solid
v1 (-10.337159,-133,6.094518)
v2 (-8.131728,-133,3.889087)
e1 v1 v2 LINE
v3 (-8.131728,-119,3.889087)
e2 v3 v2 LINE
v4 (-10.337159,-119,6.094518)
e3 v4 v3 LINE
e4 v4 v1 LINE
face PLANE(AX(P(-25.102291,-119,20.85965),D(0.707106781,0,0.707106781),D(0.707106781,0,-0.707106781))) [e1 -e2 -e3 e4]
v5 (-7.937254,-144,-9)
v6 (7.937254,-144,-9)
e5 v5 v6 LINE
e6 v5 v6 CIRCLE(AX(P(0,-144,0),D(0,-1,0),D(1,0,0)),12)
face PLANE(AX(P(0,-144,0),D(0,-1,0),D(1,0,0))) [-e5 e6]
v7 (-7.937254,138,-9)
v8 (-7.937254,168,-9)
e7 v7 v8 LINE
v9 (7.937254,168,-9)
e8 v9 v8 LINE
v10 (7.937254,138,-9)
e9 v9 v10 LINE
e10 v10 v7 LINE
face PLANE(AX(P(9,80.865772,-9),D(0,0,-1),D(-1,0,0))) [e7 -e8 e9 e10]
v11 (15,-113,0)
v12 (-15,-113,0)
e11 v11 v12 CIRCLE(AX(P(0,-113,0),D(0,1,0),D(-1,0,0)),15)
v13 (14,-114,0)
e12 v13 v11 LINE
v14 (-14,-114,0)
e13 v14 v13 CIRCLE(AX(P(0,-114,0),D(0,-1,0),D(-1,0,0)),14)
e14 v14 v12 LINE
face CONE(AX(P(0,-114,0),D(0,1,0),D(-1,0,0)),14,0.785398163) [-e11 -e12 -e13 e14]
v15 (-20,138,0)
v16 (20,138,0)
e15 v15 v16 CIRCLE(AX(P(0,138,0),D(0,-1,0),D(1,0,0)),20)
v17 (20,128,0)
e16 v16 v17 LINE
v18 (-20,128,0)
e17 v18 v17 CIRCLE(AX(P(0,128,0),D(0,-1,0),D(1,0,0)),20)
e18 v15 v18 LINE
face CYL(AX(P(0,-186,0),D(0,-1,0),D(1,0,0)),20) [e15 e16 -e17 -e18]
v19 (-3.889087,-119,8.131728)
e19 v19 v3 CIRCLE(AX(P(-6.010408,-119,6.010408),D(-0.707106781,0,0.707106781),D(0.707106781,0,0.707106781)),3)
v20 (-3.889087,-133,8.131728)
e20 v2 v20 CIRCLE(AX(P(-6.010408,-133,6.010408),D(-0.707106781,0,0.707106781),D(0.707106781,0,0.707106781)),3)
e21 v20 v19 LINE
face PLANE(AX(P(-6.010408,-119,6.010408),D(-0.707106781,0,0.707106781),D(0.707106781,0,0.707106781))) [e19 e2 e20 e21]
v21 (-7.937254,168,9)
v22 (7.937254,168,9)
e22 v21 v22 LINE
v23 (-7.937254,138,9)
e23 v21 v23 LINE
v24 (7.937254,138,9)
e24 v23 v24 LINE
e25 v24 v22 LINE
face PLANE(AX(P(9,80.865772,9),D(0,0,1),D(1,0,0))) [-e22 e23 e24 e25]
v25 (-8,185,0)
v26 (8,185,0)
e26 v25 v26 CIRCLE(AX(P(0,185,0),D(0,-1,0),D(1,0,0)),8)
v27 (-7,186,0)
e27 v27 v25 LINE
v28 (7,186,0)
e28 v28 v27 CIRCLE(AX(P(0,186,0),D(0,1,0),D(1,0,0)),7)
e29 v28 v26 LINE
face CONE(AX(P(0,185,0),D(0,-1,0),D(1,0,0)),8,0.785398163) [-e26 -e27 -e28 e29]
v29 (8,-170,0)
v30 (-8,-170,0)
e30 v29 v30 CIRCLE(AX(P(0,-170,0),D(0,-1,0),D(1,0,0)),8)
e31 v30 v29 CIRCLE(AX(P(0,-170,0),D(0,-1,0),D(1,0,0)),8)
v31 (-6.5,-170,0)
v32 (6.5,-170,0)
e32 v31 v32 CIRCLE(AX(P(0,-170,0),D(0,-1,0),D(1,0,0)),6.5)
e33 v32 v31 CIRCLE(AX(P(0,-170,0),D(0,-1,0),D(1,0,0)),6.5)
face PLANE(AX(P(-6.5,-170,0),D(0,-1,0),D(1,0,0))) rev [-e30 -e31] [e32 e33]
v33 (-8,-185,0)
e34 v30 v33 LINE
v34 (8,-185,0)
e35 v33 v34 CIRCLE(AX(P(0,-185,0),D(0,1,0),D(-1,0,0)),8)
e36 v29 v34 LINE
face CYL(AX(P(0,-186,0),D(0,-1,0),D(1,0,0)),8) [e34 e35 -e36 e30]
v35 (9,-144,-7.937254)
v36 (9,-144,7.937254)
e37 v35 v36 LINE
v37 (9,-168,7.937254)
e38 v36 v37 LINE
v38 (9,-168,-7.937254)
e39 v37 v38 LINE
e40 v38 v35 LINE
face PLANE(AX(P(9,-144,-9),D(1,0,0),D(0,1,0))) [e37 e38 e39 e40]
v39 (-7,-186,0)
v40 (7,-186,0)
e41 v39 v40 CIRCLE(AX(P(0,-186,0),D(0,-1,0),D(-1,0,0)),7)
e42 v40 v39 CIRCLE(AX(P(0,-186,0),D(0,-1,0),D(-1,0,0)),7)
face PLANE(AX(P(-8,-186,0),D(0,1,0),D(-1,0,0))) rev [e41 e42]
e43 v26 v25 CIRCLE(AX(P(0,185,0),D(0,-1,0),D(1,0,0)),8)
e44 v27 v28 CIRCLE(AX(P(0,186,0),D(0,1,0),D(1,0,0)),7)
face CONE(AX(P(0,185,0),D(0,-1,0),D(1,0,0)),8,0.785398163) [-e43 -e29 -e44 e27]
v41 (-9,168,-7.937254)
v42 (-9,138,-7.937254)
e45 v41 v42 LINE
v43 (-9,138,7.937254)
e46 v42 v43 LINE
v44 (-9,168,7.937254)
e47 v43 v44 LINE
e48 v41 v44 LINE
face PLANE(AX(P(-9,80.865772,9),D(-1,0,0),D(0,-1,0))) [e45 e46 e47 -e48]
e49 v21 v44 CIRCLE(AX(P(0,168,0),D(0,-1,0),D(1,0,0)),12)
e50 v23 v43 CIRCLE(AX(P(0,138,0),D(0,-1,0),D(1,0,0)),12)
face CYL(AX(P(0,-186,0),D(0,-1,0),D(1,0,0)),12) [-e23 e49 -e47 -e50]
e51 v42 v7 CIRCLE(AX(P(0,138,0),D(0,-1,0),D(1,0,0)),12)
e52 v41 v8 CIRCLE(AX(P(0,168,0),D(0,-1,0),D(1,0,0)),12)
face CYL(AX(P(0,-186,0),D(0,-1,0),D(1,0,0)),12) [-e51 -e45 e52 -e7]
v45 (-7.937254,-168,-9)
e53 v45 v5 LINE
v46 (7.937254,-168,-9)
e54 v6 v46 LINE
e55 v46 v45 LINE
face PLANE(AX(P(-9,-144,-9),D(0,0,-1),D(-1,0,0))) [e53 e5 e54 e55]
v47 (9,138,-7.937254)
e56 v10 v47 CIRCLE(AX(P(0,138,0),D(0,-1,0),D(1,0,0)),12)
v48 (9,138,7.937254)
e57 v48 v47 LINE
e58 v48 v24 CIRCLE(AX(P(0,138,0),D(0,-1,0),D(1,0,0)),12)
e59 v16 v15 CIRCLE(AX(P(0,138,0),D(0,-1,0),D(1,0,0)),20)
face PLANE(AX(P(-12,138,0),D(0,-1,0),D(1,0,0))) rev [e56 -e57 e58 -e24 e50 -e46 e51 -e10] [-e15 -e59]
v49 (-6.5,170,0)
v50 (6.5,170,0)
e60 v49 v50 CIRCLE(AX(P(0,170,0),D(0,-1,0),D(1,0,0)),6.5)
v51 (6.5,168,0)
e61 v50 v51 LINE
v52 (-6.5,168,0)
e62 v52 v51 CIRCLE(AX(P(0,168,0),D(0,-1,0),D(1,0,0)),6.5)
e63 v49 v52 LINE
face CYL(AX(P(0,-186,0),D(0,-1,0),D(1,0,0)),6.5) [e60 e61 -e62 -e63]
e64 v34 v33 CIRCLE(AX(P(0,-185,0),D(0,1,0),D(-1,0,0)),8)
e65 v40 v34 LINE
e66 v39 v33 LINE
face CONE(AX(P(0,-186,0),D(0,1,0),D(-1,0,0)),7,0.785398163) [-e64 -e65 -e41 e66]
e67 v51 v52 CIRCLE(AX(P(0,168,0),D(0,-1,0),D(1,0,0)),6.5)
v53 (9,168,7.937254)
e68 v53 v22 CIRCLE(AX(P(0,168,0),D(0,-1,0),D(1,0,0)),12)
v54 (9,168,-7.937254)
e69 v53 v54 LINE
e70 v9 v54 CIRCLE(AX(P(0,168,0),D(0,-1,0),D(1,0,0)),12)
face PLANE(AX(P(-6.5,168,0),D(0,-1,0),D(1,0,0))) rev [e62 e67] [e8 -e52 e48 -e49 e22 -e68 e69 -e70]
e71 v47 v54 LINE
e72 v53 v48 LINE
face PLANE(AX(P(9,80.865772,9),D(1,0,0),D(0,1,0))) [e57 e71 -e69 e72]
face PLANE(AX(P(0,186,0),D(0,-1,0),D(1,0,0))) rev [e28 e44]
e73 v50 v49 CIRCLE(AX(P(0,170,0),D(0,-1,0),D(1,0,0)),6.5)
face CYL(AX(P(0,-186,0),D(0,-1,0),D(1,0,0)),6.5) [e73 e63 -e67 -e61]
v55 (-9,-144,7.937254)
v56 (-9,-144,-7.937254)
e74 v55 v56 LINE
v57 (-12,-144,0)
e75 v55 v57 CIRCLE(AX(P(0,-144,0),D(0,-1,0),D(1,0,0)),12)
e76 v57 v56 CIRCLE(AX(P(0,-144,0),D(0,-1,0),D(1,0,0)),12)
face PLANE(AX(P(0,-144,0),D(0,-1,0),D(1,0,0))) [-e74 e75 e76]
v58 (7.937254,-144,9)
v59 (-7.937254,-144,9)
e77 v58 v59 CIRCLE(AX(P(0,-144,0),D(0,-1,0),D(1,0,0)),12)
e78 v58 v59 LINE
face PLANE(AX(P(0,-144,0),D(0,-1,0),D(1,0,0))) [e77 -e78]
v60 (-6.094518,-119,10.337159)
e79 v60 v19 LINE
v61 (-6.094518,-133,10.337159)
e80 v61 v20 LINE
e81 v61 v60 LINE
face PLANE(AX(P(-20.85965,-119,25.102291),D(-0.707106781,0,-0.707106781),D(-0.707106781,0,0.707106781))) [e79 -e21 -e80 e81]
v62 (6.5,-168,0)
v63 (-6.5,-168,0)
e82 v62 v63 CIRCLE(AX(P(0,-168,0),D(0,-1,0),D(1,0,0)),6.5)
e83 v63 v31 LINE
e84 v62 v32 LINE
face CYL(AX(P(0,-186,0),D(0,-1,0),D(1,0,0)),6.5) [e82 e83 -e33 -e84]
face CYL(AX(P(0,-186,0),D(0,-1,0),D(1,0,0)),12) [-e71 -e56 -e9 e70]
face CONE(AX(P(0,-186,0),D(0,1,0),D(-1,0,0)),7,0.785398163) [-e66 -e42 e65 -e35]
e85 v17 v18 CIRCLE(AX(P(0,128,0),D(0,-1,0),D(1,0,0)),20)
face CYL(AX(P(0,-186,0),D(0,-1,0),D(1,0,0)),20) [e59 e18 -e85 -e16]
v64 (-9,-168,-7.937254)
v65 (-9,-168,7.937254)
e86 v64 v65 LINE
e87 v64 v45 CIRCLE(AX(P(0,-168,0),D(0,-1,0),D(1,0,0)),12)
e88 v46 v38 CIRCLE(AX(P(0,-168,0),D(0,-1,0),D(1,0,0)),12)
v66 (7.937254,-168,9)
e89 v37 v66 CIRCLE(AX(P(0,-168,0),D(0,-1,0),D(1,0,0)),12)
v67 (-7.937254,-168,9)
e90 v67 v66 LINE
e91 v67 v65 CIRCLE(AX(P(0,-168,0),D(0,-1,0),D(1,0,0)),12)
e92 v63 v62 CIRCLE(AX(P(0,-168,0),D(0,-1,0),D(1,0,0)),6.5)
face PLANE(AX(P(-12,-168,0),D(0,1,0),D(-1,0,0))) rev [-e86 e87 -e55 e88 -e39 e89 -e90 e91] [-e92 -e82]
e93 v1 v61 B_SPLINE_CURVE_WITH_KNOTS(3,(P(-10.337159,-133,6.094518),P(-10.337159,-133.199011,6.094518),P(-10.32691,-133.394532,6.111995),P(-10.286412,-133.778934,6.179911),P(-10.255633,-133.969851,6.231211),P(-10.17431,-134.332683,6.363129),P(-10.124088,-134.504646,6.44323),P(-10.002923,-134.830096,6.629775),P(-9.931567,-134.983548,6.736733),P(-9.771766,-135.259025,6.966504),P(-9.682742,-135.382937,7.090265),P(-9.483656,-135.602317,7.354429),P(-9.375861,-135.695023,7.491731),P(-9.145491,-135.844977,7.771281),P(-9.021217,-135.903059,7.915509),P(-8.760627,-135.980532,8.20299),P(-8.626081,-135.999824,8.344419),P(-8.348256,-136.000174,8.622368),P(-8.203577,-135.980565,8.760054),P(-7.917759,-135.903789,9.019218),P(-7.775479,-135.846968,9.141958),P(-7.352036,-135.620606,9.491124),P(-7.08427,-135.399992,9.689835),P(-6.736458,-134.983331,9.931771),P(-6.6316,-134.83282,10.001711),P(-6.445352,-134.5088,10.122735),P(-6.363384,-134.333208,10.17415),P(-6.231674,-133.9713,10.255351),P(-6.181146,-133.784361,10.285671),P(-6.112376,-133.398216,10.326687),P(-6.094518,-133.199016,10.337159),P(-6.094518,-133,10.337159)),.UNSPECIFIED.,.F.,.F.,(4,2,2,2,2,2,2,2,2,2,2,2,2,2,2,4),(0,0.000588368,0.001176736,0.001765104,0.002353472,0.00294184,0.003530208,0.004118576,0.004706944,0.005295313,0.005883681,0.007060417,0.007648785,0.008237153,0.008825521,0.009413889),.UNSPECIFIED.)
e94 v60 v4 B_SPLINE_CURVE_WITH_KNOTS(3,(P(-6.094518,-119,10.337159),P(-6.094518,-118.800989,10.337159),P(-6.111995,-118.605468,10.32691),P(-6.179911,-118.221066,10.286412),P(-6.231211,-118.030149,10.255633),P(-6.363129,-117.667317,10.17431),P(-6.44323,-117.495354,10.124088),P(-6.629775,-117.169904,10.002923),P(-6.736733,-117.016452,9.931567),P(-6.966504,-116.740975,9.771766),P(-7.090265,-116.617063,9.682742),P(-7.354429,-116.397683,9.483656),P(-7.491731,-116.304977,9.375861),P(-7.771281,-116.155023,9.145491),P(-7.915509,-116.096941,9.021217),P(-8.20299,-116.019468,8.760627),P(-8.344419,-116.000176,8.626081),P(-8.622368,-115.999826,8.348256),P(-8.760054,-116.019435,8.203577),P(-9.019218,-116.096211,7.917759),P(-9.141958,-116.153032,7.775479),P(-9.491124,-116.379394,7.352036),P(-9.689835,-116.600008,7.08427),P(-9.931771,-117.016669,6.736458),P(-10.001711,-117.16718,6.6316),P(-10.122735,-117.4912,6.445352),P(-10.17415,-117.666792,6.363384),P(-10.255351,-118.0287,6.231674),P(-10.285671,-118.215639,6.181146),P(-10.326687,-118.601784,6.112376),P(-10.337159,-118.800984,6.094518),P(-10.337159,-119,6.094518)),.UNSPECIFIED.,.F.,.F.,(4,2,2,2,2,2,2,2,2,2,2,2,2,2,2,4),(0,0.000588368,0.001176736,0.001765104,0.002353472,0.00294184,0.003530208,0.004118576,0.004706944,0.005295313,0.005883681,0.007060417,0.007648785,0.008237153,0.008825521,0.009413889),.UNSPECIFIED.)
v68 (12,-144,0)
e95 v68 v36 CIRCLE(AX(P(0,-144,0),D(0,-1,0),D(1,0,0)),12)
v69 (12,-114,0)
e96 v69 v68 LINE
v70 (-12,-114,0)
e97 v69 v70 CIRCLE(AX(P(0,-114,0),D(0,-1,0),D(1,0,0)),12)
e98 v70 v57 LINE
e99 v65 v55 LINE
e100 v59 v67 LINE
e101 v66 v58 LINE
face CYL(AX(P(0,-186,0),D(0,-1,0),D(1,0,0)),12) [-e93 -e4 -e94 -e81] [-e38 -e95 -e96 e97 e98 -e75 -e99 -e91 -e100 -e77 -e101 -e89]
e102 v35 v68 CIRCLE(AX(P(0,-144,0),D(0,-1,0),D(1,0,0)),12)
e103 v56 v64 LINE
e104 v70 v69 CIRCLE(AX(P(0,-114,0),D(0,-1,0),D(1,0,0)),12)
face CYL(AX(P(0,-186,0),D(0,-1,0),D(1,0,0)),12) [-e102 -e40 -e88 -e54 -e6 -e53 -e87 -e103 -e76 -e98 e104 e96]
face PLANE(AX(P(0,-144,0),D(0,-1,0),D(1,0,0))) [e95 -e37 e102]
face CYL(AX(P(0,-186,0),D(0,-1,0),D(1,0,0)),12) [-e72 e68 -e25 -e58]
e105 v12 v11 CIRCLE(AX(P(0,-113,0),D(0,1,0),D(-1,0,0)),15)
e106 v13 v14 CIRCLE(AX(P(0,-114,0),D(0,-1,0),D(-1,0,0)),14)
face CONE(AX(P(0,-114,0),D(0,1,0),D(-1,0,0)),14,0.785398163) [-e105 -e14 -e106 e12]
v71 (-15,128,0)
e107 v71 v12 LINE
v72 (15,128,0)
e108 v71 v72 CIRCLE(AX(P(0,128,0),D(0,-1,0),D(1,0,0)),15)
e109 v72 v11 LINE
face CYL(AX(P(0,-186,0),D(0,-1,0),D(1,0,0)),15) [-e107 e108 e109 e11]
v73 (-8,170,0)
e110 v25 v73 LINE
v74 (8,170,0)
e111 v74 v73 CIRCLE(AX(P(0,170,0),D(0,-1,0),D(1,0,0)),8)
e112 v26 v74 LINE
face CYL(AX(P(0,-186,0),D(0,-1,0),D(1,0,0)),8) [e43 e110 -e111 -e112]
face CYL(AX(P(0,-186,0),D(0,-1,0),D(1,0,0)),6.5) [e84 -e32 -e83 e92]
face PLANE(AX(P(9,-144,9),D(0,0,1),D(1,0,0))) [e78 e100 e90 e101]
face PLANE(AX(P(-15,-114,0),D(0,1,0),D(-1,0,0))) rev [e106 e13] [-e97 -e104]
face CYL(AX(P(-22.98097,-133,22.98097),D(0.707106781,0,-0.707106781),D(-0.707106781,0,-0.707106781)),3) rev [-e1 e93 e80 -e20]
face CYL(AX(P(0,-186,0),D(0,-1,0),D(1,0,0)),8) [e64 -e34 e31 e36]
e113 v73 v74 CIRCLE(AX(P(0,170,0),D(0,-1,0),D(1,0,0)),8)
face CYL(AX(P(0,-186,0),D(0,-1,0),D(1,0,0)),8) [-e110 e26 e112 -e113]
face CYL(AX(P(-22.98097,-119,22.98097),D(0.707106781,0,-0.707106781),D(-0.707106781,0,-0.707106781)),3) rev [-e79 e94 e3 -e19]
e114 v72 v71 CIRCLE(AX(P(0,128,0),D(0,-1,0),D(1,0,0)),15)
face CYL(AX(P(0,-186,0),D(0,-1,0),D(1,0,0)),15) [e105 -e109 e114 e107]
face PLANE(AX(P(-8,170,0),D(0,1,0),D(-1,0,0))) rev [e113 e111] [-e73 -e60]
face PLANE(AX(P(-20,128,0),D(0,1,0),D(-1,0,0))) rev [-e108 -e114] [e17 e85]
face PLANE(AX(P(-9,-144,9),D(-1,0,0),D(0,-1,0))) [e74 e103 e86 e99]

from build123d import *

# Parameters (mm, degrees)
SKETCH_2_OUTSIDE_W   = 117.256
SKETCH_2_OUTSIDE_H   = 117.256
SKETCH_2_OUTSIDE_W_2 = 18
SKETCH_2_OUTSIDE_H_2 = 18
CUT_EXTRUDE_1_DEPTH  = 30
SKETCH_3_OUTSIDE_W   = 117.256
SKETCH_3_OUTSIDE_H   = 117.256
SKETCH_3_OUTSIDE_W_2 = 18
SKETCH_3_OUTSIDE_H_2 = 18
CUT_EXTRUDE_2_DEPTH  = 24
CUT_EXTRUDE_START    = 8.5
CUT_EXTRUDE_3_DEPTH  = 24
CHAMFER_1_SIZE       = 1


with BuildPart() as part:
    # 草图1 → 旋转1 (revolve)
    with BuildSketch(Plane.XY, mode=Mode.PRIVATE) as revolve_1_sk:
        Polygon((0, -186), (0, 186), (-8, 186), (-8, 170), (-6.5, 170), (-6.5, 168), (-12, 168), (-12, 138), (-20, 138), (-20, 128), (-15, 128), (-15, -114), (-12, -114), (-12, -168), (-6.5, -168), (-6.5, -170), (-8, -170), (-8, -186), align=None)
    revolve(revolve_1_sk.sketch.rotate(Axis((0, -186, 0), (0, 1, 0)), 180), axis=Axis((0, -186, 0), (0, 1, 0)))

    # 草图2 outside → 切除-拉伸1 (cut)
    with BuildSketch(Plane(origin=(0, 168, 0), x_dir=(1, 0, 0), z_dir=(0, 1, 0))):
        Rectangle(SKETCH_2_OUTSIDE_W, SKETCH_2_OUTSIDE_H)
        Rectangle(SKETCH_2_OUTSIDE_W_2, SKETCH_2_OUTSIDE_H_2, mode=Mode.SUBTRACT)
    extrude(amount=-CUT_EXTRUDE_1_DEPTH, mode=Mode.SUBTRACT)

    # 草图3 outside → 切除-拉伸2 (cut)
    with BuildSketch(Plane.XZ.offset(168)):
        Rectangle(SKETCH_3_OUTSIDE_W, SKETCH_3_OUTSIDE_H)
        Rectangle(SKETCH_3_OUTSIDE_W_2, SKETCH_3_OUTSIDE_H_2, mode=Mode.SUBTRACT)
    extrude(amount=-CUT_EXTRUDE_2_DEPTH, mode=Mode.SUBTRACT)

    # 草图4 → 切除-拉伸3 (cut)
    with BuildSketch(Plane(origin=(0, 0, 0), x_dir=(0, -1, 0), z_dir=(-0.7071067811865488, 0, 0.7071067811865464)).offset(CUT_EXTRUDE_START)):
        with BuildLine():
            Line((119, 3), (133, 3))
            ThreePointArc((133, 3), (136, 0), (133, -3))
            Line((133, -3), (119, -3))
            ThreePointArc((119, -3), (116, 0), (119, 3))
        make_face()
    extrude(amount=CUT_EXTRUDE_3_DEPTH, mode=Mode.SUBTRACT)

    # 倒角1
    chamfer_1_edges = [part.edges().sort_by_distance(p)[0] for p in [
        (-8, -186, 0),
        (-15, -114, 0),
        (-8, 186, 0),
    ]]
    chamfer(chamfer_1_edges, length=CHAMFER_1_SIZE)


solid = part.part
